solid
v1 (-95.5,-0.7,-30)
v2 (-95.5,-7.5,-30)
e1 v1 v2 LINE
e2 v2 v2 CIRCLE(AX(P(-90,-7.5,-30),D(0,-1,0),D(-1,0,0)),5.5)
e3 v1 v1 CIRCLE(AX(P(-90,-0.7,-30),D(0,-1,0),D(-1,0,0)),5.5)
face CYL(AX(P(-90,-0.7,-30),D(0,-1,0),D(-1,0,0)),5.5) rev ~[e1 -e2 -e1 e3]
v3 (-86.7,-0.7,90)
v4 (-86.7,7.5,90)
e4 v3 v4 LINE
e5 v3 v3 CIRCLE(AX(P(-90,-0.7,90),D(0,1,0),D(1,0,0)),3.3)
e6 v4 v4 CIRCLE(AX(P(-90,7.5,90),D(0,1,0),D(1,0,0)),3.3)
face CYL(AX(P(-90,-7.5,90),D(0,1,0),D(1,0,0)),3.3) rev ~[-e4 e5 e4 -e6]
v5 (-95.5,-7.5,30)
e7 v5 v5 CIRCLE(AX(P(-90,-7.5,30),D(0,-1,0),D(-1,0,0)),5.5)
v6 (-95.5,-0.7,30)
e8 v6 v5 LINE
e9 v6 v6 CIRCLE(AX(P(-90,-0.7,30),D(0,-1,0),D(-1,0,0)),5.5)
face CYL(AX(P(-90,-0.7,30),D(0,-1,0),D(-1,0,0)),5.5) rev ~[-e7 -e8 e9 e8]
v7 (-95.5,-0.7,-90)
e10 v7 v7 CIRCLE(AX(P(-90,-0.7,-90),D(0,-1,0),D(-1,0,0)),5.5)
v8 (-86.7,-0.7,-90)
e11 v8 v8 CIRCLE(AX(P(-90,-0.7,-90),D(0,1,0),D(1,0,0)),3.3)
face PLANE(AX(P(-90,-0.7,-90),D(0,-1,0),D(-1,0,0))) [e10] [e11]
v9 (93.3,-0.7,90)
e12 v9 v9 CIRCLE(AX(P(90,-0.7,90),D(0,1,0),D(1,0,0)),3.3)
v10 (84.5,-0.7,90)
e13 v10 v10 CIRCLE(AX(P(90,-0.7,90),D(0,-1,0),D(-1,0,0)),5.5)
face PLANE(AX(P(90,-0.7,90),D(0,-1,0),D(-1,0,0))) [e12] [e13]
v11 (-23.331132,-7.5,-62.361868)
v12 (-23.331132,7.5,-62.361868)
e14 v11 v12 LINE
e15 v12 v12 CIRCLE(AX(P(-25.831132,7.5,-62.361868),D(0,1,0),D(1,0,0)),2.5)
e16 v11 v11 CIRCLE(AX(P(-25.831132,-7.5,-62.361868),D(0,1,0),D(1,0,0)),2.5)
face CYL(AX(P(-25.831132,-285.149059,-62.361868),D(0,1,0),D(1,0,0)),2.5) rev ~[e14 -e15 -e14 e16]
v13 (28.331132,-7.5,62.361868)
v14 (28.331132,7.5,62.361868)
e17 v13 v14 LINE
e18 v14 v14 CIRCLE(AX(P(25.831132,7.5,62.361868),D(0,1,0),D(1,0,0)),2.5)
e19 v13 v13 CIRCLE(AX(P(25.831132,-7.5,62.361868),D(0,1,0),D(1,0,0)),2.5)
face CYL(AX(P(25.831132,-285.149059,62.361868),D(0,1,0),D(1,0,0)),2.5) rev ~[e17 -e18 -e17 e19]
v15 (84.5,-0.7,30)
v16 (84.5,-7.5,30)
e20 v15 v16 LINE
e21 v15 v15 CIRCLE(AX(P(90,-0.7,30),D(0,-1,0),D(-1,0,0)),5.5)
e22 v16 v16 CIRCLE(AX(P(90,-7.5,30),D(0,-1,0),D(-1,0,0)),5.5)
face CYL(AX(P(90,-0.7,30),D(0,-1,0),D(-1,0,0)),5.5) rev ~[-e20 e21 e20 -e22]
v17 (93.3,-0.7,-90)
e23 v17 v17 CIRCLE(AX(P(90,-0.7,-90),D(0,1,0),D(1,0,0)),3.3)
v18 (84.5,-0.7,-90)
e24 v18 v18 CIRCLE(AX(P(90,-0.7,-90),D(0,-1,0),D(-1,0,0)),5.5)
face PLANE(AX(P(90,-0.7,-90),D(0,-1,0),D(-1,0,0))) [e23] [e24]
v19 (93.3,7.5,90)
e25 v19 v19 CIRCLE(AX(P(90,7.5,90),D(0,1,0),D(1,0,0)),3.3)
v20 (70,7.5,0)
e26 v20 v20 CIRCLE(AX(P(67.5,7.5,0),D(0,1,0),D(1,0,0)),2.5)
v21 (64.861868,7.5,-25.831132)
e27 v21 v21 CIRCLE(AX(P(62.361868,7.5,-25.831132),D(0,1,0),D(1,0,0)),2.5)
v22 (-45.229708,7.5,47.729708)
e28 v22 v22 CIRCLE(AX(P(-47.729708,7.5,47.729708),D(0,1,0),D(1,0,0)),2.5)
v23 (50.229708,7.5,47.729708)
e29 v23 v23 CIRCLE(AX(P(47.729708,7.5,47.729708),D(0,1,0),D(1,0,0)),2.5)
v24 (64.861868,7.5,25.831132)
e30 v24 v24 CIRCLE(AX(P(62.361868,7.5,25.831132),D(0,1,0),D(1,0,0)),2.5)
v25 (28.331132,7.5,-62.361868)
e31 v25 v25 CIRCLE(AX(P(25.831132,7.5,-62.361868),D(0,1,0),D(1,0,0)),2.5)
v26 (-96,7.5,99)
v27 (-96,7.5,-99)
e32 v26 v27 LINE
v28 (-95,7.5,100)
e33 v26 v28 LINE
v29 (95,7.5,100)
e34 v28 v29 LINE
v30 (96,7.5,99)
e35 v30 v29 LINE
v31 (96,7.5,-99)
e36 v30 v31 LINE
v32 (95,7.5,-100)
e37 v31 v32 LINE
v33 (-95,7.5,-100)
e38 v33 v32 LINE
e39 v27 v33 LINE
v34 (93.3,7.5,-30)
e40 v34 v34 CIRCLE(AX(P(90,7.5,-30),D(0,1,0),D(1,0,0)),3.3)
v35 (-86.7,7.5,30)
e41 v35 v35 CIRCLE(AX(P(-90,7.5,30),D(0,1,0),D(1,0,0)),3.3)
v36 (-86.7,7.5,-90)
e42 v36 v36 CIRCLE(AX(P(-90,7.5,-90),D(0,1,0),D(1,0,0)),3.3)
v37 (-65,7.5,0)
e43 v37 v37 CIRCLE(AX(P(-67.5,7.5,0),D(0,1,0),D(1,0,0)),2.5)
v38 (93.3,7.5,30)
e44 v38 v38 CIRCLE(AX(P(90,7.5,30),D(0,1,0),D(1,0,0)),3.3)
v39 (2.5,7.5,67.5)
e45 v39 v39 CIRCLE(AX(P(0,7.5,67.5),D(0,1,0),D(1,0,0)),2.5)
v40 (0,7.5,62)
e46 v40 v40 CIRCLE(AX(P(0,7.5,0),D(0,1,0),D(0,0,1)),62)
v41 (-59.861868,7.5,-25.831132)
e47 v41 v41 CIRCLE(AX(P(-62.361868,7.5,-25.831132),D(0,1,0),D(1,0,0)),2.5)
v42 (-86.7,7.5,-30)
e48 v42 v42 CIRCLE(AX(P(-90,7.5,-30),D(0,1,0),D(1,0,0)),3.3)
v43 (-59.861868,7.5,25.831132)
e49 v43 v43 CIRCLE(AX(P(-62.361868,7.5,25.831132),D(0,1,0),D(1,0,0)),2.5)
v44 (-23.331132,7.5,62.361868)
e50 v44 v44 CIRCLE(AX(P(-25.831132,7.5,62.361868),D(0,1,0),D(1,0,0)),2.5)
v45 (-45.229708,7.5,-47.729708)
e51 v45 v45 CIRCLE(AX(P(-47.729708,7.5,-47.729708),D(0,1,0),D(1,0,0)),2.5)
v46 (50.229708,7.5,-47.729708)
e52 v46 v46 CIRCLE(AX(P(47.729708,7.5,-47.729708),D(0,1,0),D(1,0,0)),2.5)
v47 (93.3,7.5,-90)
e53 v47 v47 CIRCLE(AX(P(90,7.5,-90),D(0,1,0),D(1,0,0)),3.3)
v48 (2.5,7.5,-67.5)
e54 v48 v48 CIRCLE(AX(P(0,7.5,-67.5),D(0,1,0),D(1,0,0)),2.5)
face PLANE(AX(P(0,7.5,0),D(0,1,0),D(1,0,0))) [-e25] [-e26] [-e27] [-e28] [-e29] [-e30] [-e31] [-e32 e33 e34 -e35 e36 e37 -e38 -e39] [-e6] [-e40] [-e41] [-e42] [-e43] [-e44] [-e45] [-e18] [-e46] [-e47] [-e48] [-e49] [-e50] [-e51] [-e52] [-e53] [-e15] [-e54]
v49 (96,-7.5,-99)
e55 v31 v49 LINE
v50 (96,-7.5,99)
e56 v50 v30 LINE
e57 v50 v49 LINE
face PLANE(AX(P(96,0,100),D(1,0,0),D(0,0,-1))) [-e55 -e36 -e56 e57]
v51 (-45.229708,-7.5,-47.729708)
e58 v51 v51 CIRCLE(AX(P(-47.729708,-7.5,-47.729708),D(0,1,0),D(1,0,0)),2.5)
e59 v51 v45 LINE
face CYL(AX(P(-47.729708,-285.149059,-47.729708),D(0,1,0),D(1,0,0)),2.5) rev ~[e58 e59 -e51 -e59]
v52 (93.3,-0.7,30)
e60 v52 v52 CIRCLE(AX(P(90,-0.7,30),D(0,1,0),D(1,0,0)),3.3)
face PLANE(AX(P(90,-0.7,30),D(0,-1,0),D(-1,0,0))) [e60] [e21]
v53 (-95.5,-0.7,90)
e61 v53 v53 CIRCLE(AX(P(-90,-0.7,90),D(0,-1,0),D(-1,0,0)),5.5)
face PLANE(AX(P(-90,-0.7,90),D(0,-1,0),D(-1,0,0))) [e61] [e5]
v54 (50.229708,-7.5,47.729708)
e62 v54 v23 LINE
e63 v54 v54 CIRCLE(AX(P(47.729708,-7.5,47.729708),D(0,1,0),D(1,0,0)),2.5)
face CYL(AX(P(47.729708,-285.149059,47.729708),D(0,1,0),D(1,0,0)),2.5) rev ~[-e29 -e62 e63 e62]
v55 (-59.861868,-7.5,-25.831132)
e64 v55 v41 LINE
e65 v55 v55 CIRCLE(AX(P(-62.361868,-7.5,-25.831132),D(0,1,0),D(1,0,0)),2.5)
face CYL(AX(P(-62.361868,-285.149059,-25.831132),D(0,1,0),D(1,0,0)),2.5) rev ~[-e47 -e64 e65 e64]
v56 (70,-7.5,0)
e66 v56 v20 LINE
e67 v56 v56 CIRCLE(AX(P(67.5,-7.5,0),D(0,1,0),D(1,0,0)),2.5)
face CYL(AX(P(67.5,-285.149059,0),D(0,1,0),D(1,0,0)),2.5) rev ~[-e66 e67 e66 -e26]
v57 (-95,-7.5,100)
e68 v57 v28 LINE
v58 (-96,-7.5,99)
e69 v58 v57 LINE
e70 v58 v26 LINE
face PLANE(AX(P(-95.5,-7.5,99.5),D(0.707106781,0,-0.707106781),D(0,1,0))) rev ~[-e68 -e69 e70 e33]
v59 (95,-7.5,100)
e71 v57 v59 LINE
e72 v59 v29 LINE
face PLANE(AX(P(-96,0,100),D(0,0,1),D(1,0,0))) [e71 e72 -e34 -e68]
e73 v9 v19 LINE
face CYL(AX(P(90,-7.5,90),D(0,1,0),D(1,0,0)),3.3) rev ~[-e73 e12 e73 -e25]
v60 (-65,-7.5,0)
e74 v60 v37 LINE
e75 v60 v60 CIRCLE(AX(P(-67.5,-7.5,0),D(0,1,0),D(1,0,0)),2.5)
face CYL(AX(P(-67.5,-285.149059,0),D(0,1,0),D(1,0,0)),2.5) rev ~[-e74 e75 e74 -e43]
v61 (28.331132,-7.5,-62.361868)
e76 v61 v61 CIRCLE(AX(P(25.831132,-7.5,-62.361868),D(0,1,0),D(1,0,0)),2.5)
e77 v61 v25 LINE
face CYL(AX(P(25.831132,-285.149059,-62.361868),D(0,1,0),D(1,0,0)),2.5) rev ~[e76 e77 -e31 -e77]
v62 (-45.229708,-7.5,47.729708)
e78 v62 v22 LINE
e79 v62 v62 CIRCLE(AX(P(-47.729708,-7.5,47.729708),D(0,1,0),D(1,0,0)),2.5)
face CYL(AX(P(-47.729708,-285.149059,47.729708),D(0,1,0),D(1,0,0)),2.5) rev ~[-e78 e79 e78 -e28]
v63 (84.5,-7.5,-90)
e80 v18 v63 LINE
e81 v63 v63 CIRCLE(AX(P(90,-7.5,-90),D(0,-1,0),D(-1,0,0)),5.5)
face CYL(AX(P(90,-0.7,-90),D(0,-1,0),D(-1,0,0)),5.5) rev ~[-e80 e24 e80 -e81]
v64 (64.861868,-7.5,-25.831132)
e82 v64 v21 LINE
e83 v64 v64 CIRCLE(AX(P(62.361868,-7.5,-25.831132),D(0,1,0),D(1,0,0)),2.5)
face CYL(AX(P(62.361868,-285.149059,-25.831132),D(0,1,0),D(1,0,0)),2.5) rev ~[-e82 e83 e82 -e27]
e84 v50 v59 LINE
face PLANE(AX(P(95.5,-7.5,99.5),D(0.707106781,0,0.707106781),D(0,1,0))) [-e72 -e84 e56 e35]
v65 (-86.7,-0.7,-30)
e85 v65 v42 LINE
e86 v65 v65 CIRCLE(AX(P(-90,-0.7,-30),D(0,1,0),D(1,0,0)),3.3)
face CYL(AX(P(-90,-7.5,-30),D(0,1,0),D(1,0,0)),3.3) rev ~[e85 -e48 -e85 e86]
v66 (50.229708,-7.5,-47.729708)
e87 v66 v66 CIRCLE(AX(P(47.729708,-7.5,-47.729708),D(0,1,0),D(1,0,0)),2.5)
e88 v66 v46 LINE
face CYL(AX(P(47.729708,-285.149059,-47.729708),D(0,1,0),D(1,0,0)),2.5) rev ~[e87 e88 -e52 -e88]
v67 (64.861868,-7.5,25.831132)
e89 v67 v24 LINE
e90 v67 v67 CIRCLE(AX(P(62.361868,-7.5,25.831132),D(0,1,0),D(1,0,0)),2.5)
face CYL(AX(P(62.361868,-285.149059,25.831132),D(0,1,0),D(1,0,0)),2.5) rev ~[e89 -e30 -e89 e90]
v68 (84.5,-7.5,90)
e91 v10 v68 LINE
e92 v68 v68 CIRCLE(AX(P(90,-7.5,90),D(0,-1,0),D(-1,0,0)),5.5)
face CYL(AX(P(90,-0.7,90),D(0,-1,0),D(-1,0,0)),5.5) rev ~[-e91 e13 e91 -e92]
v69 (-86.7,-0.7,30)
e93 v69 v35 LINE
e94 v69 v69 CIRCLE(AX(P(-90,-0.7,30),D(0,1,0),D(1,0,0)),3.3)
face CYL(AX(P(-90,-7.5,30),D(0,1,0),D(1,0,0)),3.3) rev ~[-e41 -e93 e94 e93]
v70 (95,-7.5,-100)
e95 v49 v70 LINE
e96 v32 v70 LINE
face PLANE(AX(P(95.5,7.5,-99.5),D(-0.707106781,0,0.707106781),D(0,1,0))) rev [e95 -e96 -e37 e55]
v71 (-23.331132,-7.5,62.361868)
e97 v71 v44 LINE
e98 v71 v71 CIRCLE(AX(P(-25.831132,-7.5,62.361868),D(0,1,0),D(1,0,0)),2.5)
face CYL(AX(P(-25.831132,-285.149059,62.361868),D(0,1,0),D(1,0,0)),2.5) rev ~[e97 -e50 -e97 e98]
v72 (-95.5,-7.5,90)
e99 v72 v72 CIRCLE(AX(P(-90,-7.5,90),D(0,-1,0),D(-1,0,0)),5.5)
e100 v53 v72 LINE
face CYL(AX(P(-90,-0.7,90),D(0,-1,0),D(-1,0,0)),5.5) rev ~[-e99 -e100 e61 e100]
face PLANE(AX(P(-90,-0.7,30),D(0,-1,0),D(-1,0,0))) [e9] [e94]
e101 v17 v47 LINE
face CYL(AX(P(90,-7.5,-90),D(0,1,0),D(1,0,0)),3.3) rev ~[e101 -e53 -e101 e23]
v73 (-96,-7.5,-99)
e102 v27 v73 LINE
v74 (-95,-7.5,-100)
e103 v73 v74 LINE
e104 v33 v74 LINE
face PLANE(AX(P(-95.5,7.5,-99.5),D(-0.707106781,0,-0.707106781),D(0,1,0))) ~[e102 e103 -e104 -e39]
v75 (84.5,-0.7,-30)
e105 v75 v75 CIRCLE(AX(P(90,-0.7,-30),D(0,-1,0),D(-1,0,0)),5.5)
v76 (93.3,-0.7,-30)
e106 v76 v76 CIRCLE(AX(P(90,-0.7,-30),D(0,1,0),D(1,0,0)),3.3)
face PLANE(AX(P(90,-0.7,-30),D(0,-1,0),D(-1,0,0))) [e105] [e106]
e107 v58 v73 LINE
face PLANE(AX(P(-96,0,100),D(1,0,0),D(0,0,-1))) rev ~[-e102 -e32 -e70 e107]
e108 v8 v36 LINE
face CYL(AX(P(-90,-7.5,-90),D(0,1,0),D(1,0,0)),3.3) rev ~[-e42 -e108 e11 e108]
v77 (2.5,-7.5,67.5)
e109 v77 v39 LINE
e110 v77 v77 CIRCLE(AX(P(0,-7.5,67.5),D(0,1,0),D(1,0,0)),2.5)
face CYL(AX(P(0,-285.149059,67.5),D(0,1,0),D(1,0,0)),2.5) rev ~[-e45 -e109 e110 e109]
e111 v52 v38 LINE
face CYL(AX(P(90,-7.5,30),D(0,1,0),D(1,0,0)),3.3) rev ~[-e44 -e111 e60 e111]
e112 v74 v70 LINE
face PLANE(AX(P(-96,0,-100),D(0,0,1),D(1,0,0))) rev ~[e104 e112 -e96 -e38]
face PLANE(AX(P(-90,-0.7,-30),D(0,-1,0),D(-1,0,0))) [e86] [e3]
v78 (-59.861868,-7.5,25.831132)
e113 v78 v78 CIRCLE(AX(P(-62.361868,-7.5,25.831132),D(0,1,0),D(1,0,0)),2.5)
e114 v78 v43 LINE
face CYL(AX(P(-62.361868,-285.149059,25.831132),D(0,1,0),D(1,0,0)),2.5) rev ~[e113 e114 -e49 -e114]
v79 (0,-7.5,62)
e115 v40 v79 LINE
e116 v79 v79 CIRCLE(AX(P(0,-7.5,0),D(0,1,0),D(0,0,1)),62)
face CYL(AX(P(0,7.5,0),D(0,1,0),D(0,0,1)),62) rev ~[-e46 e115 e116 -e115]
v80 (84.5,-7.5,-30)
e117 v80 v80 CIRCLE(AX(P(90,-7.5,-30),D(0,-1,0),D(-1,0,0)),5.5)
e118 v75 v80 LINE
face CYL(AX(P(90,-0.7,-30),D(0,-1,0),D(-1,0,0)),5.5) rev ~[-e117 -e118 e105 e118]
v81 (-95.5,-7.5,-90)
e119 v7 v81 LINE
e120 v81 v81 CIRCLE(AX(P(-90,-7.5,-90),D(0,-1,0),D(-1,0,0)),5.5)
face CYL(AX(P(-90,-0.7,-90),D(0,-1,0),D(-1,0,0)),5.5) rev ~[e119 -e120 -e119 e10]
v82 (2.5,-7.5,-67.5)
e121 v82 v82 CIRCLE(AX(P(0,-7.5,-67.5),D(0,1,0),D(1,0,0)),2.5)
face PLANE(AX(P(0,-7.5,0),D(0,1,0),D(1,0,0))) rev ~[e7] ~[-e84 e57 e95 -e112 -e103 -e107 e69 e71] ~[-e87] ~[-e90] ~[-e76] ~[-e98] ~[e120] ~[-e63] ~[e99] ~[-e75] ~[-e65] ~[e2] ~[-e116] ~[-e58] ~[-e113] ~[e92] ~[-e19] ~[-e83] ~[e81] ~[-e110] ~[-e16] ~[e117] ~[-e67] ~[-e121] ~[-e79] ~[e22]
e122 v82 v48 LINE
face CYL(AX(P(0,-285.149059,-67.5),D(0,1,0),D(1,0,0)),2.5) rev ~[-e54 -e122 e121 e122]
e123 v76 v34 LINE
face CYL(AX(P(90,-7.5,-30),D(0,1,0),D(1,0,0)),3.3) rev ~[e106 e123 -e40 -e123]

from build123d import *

# Parameters (mm, degrees)
SKETCH_1_W                = 192
SKETCH_1_H                = 200
EXTRUDE_1_DEPTH           = 7.5
CHAMFER_1_SIZE            = 1
HOLE_WIZARD_1_D           = 6.6
HOLE_WIZARD_1_CBORE_D     = 11
HOLE_WIZARD_1_CBORE_DEPTH = 6.8
SKETCH_7_R                = 62
CUT_EXTRUDE_1_DEPTH       = 15
HOLE_WIZARD_M6_1_D        = 5


with BuildPart() as part:
    # 草图1 → 凸台-拉伸1 (new, symmetric)
    with BuildSketch(Plane(origin=(0, 0, 0), x_dir=(1, 0, 0), z_dir=(0, 1, 0))):
        Rectangle(SKETCH_1_W, SKETCH_1_H)
    extrude(amount=EXTRUDE_1_DEPTH, both=True)

    # 倒角1
    chamfer_1_edges = [part.edges().sort_by_distance(p)[0] for p in [
        (96, 0, 100),
        (-96, 0, 100),
        (-96, 0, -100),
        (96, 0, -100),
    ]]
    chamfer(chamfer_1_edges, length=CHAMFER_1_SIZE)

    # 打孔尺寸(%根据)内六角圆柱头螺钉的类型1 (through all)
    with Locations(Plane(origin=(0, -7.5, 0), x_dir=(-1, 0, 0), z_dir=(0, -1, 0))):
        with Locations((90, -90), (90, -30), (-90, -30), (-90, -90), (-90, 90), (-90, 30), (90, 30), (90, 90)):
            CounterBoreHole(HOLE_WIZARD_1_D / 2, HOLE_WIZARD_1_CBORE_D / 2, HOLE_WIZARD_1_CBORE_DEPTH)

    # 草图7 → 切除-拉伸1 (cut)
    with BuildSketch(Plane(origin=(0, 7.5, 0), x_dir=(1, 0, 0), z_dir=(0, 1, 0))):
        with Locations(Location((0, 0, 0), (0, 0, 270))):
            Circle(SKETCH_7_R)
    extrude(amount=-CUT_EXTRUDE_1_DEPTH, mode=Mode.SUBTRACT)

    # M6 螺纹孔1 (through all)
    with Locations(Plane(origin=(0, -7.5, 0), x_dir=(-1, 0, 0), z_dir=(0, -1, 0))):
        with Locations((67.5, 0), (62.361868445, -25.831131685), (47.72970773, -47.72970773), (25.831131685, -62.361868445), (0, -67.5), (-25.831131685, -62.361868445), (-47.72970773, -47.72970773), (-62.361868445, -25.831131685), (-67.5, 0), (-62.361868445, 25.831131685), (-47.72970773, 47.72970773), (-25.831131685, 62.361868445), (0, 67.5), (25.831131685, 62.361868445), (47.72970773, 47.72970773), (62.361868445, 25.831131685)):
            Hole(HOLE_WIZARD_M6_1_D / 2)


solid = part.part
